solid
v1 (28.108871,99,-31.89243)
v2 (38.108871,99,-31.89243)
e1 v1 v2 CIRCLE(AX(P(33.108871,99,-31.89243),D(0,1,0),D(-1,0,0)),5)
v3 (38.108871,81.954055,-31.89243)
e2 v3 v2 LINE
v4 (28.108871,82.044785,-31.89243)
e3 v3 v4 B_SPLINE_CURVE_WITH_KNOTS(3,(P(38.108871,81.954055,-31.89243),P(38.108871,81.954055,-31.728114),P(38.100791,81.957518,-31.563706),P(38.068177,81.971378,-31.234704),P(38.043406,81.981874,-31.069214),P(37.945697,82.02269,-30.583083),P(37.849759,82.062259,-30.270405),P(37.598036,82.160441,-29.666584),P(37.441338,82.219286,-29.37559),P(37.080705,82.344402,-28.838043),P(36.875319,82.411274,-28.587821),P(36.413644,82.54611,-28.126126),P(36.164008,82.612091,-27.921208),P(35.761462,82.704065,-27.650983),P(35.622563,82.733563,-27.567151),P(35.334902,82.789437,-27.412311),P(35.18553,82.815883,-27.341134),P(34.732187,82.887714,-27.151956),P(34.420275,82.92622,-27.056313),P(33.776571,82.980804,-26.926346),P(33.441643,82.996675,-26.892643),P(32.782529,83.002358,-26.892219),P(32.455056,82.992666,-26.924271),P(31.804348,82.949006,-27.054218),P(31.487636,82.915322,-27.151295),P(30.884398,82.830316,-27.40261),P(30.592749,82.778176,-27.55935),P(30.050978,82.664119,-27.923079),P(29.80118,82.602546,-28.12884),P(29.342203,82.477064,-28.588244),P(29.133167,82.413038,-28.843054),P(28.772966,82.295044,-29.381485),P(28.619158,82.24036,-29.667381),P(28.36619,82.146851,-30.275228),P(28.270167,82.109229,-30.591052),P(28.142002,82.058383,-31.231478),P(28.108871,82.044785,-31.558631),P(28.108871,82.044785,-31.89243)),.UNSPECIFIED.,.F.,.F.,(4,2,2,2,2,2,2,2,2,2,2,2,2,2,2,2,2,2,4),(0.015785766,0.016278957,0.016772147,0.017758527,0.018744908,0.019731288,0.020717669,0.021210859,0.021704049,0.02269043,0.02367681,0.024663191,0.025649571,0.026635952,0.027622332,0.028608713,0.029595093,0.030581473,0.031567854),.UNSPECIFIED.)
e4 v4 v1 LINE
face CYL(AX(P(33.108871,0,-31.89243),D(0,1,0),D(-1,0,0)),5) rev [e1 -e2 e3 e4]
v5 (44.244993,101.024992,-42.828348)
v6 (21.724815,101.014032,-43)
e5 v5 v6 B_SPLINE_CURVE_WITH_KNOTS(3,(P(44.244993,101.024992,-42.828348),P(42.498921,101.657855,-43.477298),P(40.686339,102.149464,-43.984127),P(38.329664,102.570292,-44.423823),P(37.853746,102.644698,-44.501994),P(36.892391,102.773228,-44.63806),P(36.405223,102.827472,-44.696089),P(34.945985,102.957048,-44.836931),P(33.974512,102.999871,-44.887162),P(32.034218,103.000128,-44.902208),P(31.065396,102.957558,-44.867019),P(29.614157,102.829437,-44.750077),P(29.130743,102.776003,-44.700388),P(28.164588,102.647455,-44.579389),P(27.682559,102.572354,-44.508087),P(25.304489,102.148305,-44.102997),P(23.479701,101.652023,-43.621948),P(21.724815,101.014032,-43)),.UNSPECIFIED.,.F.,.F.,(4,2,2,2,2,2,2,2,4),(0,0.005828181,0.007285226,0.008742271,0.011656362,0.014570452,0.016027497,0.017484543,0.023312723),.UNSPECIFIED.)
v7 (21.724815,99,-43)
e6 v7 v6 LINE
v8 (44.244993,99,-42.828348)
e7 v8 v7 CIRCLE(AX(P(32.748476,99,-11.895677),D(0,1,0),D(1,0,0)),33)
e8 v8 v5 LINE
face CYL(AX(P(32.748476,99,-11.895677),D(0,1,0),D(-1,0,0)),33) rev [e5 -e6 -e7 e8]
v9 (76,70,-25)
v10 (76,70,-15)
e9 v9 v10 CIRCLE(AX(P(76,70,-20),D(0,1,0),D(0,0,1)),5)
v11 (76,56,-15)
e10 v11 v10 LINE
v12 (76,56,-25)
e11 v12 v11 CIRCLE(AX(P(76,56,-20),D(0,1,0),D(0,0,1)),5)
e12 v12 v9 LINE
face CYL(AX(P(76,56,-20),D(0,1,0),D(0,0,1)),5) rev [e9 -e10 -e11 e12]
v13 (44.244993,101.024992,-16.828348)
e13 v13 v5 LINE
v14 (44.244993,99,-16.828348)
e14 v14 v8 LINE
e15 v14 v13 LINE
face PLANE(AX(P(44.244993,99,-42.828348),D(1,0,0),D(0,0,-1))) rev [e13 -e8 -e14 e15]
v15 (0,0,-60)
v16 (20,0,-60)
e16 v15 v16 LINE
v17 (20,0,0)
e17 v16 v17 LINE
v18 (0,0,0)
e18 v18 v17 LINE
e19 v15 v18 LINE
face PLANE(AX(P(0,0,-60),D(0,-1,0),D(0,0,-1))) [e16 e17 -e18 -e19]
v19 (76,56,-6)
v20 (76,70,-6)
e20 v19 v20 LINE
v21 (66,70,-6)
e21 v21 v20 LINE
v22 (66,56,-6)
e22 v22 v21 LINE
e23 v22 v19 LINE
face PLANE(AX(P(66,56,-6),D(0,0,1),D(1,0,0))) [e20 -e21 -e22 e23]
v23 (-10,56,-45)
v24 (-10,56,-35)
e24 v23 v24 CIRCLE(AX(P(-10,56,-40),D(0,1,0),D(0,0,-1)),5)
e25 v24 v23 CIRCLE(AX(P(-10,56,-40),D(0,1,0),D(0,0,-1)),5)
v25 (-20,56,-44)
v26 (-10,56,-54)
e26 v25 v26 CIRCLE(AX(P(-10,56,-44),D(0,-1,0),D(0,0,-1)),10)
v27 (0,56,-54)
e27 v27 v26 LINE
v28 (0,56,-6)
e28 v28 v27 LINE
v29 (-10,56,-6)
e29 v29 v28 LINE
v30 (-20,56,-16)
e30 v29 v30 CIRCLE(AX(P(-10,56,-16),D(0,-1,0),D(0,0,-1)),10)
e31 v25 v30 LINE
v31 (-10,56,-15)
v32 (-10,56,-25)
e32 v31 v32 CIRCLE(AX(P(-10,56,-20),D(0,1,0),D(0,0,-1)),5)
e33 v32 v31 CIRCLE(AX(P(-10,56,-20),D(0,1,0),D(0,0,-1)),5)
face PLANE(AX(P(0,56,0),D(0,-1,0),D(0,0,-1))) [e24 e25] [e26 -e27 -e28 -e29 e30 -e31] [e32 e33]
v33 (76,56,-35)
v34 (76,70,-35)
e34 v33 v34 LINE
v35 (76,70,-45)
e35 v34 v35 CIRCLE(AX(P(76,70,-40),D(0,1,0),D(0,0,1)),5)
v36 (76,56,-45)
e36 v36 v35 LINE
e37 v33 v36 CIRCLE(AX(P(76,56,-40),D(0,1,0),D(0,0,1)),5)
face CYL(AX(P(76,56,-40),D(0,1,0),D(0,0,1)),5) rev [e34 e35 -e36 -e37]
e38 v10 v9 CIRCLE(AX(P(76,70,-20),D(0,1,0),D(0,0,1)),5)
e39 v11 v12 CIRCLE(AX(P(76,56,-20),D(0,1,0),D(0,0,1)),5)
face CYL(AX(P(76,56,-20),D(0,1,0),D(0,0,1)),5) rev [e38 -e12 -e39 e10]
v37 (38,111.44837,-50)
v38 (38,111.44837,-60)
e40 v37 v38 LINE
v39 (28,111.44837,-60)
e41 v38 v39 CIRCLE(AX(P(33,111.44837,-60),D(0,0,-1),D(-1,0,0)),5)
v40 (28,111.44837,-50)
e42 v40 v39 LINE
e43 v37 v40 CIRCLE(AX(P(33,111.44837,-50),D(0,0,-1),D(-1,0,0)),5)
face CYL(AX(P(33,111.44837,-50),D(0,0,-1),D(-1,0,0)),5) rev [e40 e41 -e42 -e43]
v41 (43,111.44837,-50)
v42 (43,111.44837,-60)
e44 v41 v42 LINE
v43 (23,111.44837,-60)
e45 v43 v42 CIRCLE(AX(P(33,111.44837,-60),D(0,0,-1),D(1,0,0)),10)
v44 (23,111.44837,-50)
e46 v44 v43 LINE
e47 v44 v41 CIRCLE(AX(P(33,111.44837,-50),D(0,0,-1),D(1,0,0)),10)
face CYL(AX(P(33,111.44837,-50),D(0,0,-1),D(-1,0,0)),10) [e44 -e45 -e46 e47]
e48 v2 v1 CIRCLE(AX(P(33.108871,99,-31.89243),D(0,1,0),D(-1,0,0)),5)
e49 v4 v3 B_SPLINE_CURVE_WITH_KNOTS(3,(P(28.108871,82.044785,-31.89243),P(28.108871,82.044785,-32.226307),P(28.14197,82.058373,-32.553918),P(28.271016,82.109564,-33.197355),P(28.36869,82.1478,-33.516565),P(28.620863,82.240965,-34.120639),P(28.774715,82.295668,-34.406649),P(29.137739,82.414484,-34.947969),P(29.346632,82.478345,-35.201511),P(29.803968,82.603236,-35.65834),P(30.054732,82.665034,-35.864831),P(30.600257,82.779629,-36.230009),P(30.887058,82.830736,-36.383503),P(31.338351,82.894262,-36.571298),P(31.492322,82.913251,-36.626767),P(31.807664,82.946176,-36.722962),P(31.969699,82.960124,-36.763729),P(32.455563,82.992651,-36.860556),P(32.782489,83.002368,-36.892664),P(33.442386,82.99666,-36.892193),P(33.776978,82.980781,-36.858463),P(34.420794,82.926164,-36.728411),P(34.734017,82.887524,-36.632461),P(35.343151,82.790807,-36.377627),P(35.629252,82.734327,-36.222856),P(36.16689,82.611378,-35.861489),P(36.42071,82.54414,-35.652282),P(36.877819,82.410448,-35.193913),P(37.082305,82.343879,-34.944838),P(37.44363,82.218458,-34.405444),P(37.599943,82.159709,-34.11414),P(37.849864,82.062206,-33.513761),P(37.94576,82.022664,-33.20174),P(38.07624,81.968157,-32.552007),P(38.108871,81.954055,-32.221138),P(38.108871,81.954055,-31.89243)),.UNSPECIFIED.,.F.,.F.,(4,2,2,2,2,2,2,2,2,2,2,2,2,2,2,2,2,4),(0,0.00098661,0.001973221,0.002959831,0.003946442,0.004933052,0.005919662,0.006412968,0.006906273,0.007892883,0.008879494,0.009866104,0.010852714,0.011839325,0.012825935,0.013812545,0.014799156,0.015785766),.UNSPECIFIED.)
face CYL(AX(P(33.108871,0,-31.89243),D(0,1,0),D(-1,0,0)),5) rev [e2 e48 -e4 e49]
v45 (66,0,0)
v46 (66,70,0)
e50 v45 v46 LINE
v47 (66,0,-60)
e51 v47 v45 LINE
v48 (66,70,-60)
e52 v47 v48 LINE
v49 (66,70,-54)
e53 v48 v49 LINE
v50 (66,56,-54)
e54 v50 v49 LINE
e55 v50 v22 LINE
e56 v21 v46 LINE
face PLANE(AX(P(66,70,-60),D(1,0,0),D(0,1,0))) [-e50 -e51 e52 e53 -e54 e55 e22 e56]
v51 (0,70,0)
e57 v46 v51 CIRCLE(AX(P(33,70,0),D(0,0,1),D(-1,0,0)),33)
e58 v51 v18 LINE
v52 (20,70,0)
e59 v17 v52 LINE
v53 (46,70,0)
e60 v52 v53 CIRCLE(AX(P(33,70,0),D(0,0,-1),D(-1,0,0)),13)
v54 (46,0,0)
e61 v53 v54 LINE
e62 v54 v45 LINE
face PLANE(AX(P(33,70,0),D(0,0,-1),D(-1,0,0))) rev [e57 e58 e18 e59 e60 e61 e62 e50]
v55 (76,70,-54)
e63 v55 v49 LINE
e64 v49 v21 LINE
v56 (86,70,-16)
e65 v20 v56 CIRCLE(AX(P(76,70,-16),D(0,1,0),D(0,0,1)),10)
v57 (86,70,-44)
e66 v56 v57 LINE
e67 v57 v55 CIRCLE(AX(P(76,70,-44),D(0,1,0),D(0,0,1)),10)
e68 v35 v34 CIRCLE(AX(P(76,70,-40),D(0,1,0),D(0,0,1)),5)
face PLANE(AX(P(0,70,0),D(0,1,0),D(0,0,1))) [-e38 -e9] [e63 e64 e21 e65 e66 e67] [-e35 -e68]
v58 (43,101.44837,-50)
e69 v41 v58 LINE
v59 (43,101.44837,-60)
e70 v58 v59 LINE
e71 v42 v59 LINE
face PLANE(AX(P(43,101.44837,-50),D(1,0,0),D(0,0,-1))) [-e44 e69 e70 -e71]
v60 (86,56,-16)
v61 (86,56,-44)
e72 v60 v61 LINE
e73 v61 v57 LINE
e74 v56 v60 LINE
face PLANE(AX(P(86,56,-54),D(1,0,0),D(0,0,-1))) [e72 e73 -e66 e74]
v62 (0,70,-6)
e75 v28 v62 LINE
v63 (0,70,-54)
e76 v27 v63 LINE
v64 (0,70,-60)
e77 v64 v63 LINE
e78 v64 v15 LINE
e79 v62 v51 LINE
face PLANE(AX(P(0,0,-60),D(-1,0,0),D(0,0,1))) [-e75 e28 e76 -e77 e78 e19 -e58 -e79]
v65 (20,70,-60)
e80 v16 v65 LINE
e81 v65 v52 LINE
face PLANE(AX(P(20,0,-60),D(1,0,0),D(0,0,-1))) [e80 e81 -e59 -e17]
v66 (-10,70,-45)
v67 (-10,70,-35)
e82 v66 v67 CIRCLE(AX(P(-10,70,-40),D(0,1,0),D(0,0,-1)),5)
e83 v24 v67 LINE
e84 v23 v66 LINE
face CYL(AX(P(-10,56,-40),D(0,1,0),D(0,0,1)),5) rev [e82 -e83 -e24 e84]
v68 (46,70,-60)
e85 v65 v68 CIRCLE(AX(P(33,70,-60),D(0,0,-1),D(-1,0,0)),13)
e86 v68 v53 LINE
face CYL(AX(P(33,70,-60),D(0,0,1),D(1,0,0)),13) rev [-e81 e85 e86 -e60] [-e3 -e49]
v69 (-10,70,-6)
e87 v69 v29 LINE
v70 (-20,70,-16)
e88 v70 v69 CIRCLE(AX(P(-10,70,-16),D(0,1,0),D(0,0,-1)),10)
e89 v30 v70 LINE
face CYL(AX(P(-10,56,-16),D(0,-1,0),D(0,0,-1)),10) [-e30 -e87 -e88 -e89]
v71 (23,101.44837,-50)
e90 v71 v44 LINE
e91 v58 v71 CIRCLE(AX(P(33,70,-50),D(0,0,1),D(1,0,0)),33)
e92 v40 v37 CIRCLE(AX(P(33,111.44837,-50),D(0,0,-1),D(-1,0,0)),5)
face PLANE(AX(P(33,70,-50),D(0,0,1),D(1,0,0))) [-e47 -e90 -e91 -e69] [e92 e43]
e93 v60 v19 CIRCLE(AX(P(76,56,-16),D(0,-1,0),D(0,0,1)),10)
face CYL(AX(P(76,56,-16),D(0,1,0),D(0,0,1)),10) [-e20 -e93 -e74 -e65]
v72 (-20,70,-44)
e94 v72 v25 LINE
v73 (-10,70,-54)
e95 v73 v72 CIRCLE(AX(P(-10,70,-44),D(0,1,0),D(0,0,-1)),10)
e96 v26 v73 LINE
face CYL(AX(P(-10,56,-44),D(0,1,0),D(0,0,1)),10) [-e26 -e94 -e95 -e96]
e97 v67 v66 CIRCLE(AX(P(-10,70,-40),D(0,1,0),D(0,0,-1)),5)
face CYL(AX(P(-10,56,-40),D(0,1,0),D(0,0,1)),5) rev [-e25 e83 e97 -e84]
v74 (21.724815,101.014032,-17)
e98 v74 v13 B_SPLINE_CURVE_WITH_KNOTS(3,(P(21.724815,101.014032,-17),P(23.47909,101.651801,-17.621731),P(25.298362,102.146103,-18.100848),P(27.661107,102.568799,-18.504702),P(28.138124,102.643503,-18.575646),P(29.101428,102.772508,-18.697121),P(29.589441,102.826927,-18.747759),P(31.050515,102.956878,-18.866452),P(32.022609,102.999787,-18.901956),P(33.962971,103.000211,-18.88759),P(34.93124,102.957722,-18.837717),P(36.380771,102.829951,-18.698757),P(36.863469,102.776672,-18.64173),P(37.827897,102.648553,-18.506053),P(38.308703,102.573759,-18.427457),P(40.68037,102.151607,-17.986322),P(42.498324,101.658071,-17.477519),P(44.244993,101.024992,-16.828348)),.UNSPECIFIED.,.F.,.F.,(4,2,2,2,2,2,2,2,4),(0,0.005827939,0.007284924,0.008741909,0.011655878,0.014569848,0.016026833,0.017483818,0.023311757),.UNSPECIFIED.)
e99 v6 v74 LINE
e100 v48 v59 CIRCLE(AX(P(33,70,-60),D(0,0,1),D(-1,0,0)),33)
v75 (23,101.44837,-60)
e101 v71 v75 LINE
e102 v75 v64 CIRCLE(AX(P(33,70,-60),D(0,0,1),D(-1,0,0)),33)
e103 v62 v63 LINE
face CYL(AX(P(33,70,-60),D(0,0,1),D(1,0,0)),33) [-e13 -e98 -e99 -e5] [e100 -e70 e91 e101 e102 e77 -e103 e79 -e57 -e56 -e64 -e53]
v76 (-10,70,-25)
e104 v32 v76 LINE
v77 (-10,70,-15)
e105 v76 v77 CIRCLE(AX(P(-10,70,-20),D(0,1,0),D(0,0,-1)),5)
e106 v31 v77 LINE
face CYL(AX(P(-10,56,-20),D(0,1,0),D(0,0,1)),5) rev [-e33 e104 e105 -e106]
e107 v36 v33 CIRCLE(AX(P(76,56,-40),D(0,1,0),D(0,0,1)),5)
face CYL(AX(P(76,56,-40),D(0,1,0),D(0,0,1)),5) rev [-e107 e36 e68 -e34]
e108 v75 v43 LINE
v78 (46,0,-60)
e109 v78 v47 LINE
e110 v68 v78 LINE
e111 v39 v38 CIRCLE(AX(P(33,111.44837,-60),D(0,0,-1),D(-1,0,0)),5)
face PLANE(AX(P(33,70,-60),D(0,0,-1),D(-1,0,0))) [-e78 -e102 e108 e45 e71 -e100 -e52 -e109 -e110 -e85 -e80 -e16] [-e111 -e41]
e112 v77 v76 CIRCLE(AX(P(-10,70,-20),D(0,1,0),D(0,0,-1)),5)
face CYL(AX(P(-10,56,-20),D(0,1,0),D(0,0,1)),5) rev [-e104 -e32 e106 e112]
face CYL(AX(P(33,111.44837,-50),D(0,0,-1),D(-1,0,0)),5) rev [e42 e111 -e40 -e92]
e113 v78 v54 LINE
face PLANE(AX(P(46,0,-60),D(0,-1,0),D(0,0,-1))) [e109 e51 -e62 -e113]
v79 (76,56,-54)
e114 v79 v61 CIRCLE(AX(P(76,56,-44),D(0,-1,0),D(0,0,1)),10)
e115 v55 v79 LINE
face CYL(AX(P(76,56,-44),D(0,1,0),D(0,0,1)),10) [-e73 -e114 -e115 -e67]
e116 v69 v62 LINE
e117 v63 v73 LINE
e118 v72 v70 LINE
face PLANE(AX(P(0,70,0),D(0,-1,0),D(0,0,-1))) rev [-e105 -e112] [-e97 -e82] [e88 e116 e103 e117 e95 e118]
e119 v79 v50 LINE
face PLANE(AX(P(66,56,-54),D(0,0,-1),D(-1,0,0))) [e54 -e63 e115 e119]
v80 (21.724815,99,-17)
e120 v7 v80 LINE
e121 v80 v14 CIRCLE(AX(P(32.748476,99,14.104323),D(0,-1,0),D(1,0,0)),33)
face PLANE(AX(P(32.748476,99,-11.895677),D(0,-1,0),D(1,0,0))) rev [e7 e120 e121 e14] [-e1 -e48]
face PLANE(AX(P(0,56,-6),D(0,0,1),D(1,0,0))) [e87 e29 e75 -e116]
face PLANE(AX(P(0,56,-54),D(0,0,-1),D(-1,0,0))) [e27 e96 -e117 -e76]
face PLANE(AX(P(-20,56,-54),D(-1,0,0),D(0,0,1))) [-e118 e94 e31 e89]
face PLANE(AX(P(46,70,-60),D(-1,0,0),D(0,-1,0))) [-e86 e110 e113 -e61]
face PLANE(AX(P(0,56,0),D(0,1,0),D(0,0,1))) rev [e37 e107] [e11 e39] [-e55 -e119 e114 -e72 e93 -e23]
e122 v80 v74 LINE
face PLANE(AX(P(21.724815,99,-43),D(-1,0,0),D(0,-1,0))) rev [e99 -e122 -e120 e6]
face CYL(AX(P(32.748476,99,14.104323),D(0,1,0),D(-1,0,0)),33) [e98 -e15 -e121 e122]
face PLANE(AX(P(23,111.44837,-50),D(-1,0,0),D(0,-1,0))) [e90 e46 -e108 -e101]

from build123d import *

# Parameters (mm, degrees)
HOUSING_BODY_60_DEPTH        = 60
LIFTING_START                = -10
LIFTING_LUG_SKETCH_R         = 5
LIFTING_LUG_DEPTH            = 10
MOUNTING_FLANGES_SKETCH_W    = 20
MOUNTING_FLANGES_SKETCH_H    = 48
MOUNTING_FLANGES_SKETCH_R    = 5
MOUNTING_FLANGES_14_DEPTH    = 14
FLANGE_CORNER_FILLET_R10_A_R = 10
FLANGE_CORNER_FILLET_R10_B_R = 10
FLANGE_CORNER_FILLET_R10_C_R = 10
FLANGE_CORNER_FILLET_R10_D_R = 10
TOP_RECESS_4_DEEP_DEPTH      = 4
RECESS_HOLE_SKETCH_R         = 5
RECESS_HOLE_DEPTH            = 145.211650056


with BuildPart() as part:
    # Body Profile Sketch → Housing Body 60 (new body)
    with BuildSketch(Plane.XY):
        with BuildLine():
            Line((0, 0), (0, 70))
            ThreePointArc((0, 70), (33, 103), (66, 70))
            Line((66, 70), (66, 0))
            Line((66, 0), (46, 0))
            Line((46, 0), (46, 70))
            ThreePointArc((46, 70), (33, 83), (20, 70))
            Line((20, 70), (20, 0))
            Line((20, 0), (0, 0))
        make_face()
    extrude(amount=-HOUSING_BODY_60_DEPTH)

    # Lifting Lug Sketch → Lifting Lug (add)
    with BuildSketch(Plane(origin=(0, 0, -60), x_dir=(-1, 0, 0), z_dir=(0, 0, -1)).offset(LIFTING_START)):
        with BuildLine():
            Line((-43, 101.448370387), (-43, 111.448370387))
            ThreePointArc((-43, 111.448370387), (-33, 121.448370387), (-23, 111.448370387))
            Line((-23, 111.448370387), (-23, 101.448370387))
            ThreePointArc((-23, 101.448370387), (-33, 103), (-43, 101.448370387))
        make_face()
        with Locations((-33, 111.448370387)):
            Circle(LIFTING_LUG_SKETCH_R, mode=Mode.SUBTRACT)
    extrude(amount=LIFTING_LUG_DEPTH)

    # Mounting Flanges Sketch → Mounting Flanges 14 (add)
    # profile 1 of 2: a face of its own
    with BuildSketch(Plane(origin=(0, 70, 0), x_dir=(1, 0, 0), z_dir=(0, 1, 0))):
        with Locations((76, 30)):
            Rectangle(MOUNTING_FLANGES_SKETCH_W, MOUNTING_FLANGES_SKETCH_H)
        with Locations(Location((76, 20, 0), (0, 0, 270))):
            Circle(MOUNTING_FLANGES_SKETCH_R, mode=Mode.SUBTRACT)
        with Locations(Location((76, 40, 0), (0, 0, 270))):
            Circle(MOUNTING_FLANGES_SKETCH_R, mode=Mode.SUBTRACT)
    # profile 2 of 2: a face of its own
    with BuildSketch(Plane(origin=(0, 70, 0), x_dir=(1, 0, 0), z_dir=(0, 1, 0))):
        with Locations((-10, 30)):
            Rectangle(MOUNTING_FLANGES_SKETCH_W, MOUNTING_FLANGES_SKETCH_H)
        with Locations(Location((-10, 40, 0), (0, 0, 90))):
            Circle(MOUNTING_FLANGES_SKETCH_R, mode=Mode.SUBTRACT)
        with Locations(Location((-10, 20, 0), (0, 0, 90))):
            Circle(MOUNTING_FLANGES_SKETCH_R, mode=Mode.SUBTRACT)
    extrude(amount=-MOUNTING_FLANGES_14_DEPTH)

    # Flange Corner Fillet R10 A
    flange_corner_fillet_r10_a_edges = [part.edges().sort_by_distance(p)[0] for p in [
        (86, 63, -54),
    ]]
    fillet(flange_corner_fillet_r10_a_edges, radius=FLANGE_CORNER_FILLET_R10_A_R)

    # Flange Corner Fillet R10 B
    flange_corner_fillet_r10_b_edges = [part.edges().sort_by_distance(p)[0] for p in [
        (86, 63, -6),
    ]]
    fillet(flange_corner_fillet_r10_b_edges, radius=FLANGE_CORNER_FILLET_R10_B_R)

    # Flange Corner Fillet R10 C
    flange_corner_fillet_r10_c_edges = [part.edges().sort_by_distance(p)[0] for p in [
        (-20, 63, -54),
    ]]
    fillet(flange_corner_fillet_r10_c_edges, radius=FLANGE_CORNER_FILLET_R10_C_R)

    # Flange Corner Fillet R10 D
    flange_corner_fillet_r10_d_edges = [part.edges().sort_by_distance(p)[0] for p in [
        (-20, 63, -6),
    ]]
    fillet(flange_corner_fillet_r10_d_edges, radius=FLANGE_CORNER_FILLET_R10_D_R)

    # Top Recess Sketch → Top Recess 4 Deep (cut)
    with BuildSketch(Plane(origin=(0, 103, 0), x_dir=(1, 0, 0), z_dir=(0, 1, 0))):
        with BuildLine():
            Line((21.724814581, 43), (21.724814581, 17))
            ThreePointArc((21.724814581, 17), (33, 18.894718879), (44.244993393, 16.828347794))
            Line((44.244993393, 16.828347794), (44.244993393, 42.828347794))
            ThreePointArc((44.244993393, 42.828347794), (33, 44.894718879), (21.724814581, 43))
        make_face()
    extrude(amount=-TOP_RECESS_4_DEEP_DEPTH, mode=Mode.SUBTRACT)

    # Recess Hole Sketch → Recess Hole (cut, through all)
    with BuildSketch(Plane(origin=(0, 99, 0), x_dir=(1, 0, 0), z_dir=(0, 1, 0))):
        with Locations(Location((33.108870808, 31.892430073, 0), (0, 0, 180))):
            Circle(RECESS_HOLE_SKETCH_R)
    extrude(amount=-RECESS_HOLE_DEPTH, mode=Mode.SUBTRACT)


solid = part.part
